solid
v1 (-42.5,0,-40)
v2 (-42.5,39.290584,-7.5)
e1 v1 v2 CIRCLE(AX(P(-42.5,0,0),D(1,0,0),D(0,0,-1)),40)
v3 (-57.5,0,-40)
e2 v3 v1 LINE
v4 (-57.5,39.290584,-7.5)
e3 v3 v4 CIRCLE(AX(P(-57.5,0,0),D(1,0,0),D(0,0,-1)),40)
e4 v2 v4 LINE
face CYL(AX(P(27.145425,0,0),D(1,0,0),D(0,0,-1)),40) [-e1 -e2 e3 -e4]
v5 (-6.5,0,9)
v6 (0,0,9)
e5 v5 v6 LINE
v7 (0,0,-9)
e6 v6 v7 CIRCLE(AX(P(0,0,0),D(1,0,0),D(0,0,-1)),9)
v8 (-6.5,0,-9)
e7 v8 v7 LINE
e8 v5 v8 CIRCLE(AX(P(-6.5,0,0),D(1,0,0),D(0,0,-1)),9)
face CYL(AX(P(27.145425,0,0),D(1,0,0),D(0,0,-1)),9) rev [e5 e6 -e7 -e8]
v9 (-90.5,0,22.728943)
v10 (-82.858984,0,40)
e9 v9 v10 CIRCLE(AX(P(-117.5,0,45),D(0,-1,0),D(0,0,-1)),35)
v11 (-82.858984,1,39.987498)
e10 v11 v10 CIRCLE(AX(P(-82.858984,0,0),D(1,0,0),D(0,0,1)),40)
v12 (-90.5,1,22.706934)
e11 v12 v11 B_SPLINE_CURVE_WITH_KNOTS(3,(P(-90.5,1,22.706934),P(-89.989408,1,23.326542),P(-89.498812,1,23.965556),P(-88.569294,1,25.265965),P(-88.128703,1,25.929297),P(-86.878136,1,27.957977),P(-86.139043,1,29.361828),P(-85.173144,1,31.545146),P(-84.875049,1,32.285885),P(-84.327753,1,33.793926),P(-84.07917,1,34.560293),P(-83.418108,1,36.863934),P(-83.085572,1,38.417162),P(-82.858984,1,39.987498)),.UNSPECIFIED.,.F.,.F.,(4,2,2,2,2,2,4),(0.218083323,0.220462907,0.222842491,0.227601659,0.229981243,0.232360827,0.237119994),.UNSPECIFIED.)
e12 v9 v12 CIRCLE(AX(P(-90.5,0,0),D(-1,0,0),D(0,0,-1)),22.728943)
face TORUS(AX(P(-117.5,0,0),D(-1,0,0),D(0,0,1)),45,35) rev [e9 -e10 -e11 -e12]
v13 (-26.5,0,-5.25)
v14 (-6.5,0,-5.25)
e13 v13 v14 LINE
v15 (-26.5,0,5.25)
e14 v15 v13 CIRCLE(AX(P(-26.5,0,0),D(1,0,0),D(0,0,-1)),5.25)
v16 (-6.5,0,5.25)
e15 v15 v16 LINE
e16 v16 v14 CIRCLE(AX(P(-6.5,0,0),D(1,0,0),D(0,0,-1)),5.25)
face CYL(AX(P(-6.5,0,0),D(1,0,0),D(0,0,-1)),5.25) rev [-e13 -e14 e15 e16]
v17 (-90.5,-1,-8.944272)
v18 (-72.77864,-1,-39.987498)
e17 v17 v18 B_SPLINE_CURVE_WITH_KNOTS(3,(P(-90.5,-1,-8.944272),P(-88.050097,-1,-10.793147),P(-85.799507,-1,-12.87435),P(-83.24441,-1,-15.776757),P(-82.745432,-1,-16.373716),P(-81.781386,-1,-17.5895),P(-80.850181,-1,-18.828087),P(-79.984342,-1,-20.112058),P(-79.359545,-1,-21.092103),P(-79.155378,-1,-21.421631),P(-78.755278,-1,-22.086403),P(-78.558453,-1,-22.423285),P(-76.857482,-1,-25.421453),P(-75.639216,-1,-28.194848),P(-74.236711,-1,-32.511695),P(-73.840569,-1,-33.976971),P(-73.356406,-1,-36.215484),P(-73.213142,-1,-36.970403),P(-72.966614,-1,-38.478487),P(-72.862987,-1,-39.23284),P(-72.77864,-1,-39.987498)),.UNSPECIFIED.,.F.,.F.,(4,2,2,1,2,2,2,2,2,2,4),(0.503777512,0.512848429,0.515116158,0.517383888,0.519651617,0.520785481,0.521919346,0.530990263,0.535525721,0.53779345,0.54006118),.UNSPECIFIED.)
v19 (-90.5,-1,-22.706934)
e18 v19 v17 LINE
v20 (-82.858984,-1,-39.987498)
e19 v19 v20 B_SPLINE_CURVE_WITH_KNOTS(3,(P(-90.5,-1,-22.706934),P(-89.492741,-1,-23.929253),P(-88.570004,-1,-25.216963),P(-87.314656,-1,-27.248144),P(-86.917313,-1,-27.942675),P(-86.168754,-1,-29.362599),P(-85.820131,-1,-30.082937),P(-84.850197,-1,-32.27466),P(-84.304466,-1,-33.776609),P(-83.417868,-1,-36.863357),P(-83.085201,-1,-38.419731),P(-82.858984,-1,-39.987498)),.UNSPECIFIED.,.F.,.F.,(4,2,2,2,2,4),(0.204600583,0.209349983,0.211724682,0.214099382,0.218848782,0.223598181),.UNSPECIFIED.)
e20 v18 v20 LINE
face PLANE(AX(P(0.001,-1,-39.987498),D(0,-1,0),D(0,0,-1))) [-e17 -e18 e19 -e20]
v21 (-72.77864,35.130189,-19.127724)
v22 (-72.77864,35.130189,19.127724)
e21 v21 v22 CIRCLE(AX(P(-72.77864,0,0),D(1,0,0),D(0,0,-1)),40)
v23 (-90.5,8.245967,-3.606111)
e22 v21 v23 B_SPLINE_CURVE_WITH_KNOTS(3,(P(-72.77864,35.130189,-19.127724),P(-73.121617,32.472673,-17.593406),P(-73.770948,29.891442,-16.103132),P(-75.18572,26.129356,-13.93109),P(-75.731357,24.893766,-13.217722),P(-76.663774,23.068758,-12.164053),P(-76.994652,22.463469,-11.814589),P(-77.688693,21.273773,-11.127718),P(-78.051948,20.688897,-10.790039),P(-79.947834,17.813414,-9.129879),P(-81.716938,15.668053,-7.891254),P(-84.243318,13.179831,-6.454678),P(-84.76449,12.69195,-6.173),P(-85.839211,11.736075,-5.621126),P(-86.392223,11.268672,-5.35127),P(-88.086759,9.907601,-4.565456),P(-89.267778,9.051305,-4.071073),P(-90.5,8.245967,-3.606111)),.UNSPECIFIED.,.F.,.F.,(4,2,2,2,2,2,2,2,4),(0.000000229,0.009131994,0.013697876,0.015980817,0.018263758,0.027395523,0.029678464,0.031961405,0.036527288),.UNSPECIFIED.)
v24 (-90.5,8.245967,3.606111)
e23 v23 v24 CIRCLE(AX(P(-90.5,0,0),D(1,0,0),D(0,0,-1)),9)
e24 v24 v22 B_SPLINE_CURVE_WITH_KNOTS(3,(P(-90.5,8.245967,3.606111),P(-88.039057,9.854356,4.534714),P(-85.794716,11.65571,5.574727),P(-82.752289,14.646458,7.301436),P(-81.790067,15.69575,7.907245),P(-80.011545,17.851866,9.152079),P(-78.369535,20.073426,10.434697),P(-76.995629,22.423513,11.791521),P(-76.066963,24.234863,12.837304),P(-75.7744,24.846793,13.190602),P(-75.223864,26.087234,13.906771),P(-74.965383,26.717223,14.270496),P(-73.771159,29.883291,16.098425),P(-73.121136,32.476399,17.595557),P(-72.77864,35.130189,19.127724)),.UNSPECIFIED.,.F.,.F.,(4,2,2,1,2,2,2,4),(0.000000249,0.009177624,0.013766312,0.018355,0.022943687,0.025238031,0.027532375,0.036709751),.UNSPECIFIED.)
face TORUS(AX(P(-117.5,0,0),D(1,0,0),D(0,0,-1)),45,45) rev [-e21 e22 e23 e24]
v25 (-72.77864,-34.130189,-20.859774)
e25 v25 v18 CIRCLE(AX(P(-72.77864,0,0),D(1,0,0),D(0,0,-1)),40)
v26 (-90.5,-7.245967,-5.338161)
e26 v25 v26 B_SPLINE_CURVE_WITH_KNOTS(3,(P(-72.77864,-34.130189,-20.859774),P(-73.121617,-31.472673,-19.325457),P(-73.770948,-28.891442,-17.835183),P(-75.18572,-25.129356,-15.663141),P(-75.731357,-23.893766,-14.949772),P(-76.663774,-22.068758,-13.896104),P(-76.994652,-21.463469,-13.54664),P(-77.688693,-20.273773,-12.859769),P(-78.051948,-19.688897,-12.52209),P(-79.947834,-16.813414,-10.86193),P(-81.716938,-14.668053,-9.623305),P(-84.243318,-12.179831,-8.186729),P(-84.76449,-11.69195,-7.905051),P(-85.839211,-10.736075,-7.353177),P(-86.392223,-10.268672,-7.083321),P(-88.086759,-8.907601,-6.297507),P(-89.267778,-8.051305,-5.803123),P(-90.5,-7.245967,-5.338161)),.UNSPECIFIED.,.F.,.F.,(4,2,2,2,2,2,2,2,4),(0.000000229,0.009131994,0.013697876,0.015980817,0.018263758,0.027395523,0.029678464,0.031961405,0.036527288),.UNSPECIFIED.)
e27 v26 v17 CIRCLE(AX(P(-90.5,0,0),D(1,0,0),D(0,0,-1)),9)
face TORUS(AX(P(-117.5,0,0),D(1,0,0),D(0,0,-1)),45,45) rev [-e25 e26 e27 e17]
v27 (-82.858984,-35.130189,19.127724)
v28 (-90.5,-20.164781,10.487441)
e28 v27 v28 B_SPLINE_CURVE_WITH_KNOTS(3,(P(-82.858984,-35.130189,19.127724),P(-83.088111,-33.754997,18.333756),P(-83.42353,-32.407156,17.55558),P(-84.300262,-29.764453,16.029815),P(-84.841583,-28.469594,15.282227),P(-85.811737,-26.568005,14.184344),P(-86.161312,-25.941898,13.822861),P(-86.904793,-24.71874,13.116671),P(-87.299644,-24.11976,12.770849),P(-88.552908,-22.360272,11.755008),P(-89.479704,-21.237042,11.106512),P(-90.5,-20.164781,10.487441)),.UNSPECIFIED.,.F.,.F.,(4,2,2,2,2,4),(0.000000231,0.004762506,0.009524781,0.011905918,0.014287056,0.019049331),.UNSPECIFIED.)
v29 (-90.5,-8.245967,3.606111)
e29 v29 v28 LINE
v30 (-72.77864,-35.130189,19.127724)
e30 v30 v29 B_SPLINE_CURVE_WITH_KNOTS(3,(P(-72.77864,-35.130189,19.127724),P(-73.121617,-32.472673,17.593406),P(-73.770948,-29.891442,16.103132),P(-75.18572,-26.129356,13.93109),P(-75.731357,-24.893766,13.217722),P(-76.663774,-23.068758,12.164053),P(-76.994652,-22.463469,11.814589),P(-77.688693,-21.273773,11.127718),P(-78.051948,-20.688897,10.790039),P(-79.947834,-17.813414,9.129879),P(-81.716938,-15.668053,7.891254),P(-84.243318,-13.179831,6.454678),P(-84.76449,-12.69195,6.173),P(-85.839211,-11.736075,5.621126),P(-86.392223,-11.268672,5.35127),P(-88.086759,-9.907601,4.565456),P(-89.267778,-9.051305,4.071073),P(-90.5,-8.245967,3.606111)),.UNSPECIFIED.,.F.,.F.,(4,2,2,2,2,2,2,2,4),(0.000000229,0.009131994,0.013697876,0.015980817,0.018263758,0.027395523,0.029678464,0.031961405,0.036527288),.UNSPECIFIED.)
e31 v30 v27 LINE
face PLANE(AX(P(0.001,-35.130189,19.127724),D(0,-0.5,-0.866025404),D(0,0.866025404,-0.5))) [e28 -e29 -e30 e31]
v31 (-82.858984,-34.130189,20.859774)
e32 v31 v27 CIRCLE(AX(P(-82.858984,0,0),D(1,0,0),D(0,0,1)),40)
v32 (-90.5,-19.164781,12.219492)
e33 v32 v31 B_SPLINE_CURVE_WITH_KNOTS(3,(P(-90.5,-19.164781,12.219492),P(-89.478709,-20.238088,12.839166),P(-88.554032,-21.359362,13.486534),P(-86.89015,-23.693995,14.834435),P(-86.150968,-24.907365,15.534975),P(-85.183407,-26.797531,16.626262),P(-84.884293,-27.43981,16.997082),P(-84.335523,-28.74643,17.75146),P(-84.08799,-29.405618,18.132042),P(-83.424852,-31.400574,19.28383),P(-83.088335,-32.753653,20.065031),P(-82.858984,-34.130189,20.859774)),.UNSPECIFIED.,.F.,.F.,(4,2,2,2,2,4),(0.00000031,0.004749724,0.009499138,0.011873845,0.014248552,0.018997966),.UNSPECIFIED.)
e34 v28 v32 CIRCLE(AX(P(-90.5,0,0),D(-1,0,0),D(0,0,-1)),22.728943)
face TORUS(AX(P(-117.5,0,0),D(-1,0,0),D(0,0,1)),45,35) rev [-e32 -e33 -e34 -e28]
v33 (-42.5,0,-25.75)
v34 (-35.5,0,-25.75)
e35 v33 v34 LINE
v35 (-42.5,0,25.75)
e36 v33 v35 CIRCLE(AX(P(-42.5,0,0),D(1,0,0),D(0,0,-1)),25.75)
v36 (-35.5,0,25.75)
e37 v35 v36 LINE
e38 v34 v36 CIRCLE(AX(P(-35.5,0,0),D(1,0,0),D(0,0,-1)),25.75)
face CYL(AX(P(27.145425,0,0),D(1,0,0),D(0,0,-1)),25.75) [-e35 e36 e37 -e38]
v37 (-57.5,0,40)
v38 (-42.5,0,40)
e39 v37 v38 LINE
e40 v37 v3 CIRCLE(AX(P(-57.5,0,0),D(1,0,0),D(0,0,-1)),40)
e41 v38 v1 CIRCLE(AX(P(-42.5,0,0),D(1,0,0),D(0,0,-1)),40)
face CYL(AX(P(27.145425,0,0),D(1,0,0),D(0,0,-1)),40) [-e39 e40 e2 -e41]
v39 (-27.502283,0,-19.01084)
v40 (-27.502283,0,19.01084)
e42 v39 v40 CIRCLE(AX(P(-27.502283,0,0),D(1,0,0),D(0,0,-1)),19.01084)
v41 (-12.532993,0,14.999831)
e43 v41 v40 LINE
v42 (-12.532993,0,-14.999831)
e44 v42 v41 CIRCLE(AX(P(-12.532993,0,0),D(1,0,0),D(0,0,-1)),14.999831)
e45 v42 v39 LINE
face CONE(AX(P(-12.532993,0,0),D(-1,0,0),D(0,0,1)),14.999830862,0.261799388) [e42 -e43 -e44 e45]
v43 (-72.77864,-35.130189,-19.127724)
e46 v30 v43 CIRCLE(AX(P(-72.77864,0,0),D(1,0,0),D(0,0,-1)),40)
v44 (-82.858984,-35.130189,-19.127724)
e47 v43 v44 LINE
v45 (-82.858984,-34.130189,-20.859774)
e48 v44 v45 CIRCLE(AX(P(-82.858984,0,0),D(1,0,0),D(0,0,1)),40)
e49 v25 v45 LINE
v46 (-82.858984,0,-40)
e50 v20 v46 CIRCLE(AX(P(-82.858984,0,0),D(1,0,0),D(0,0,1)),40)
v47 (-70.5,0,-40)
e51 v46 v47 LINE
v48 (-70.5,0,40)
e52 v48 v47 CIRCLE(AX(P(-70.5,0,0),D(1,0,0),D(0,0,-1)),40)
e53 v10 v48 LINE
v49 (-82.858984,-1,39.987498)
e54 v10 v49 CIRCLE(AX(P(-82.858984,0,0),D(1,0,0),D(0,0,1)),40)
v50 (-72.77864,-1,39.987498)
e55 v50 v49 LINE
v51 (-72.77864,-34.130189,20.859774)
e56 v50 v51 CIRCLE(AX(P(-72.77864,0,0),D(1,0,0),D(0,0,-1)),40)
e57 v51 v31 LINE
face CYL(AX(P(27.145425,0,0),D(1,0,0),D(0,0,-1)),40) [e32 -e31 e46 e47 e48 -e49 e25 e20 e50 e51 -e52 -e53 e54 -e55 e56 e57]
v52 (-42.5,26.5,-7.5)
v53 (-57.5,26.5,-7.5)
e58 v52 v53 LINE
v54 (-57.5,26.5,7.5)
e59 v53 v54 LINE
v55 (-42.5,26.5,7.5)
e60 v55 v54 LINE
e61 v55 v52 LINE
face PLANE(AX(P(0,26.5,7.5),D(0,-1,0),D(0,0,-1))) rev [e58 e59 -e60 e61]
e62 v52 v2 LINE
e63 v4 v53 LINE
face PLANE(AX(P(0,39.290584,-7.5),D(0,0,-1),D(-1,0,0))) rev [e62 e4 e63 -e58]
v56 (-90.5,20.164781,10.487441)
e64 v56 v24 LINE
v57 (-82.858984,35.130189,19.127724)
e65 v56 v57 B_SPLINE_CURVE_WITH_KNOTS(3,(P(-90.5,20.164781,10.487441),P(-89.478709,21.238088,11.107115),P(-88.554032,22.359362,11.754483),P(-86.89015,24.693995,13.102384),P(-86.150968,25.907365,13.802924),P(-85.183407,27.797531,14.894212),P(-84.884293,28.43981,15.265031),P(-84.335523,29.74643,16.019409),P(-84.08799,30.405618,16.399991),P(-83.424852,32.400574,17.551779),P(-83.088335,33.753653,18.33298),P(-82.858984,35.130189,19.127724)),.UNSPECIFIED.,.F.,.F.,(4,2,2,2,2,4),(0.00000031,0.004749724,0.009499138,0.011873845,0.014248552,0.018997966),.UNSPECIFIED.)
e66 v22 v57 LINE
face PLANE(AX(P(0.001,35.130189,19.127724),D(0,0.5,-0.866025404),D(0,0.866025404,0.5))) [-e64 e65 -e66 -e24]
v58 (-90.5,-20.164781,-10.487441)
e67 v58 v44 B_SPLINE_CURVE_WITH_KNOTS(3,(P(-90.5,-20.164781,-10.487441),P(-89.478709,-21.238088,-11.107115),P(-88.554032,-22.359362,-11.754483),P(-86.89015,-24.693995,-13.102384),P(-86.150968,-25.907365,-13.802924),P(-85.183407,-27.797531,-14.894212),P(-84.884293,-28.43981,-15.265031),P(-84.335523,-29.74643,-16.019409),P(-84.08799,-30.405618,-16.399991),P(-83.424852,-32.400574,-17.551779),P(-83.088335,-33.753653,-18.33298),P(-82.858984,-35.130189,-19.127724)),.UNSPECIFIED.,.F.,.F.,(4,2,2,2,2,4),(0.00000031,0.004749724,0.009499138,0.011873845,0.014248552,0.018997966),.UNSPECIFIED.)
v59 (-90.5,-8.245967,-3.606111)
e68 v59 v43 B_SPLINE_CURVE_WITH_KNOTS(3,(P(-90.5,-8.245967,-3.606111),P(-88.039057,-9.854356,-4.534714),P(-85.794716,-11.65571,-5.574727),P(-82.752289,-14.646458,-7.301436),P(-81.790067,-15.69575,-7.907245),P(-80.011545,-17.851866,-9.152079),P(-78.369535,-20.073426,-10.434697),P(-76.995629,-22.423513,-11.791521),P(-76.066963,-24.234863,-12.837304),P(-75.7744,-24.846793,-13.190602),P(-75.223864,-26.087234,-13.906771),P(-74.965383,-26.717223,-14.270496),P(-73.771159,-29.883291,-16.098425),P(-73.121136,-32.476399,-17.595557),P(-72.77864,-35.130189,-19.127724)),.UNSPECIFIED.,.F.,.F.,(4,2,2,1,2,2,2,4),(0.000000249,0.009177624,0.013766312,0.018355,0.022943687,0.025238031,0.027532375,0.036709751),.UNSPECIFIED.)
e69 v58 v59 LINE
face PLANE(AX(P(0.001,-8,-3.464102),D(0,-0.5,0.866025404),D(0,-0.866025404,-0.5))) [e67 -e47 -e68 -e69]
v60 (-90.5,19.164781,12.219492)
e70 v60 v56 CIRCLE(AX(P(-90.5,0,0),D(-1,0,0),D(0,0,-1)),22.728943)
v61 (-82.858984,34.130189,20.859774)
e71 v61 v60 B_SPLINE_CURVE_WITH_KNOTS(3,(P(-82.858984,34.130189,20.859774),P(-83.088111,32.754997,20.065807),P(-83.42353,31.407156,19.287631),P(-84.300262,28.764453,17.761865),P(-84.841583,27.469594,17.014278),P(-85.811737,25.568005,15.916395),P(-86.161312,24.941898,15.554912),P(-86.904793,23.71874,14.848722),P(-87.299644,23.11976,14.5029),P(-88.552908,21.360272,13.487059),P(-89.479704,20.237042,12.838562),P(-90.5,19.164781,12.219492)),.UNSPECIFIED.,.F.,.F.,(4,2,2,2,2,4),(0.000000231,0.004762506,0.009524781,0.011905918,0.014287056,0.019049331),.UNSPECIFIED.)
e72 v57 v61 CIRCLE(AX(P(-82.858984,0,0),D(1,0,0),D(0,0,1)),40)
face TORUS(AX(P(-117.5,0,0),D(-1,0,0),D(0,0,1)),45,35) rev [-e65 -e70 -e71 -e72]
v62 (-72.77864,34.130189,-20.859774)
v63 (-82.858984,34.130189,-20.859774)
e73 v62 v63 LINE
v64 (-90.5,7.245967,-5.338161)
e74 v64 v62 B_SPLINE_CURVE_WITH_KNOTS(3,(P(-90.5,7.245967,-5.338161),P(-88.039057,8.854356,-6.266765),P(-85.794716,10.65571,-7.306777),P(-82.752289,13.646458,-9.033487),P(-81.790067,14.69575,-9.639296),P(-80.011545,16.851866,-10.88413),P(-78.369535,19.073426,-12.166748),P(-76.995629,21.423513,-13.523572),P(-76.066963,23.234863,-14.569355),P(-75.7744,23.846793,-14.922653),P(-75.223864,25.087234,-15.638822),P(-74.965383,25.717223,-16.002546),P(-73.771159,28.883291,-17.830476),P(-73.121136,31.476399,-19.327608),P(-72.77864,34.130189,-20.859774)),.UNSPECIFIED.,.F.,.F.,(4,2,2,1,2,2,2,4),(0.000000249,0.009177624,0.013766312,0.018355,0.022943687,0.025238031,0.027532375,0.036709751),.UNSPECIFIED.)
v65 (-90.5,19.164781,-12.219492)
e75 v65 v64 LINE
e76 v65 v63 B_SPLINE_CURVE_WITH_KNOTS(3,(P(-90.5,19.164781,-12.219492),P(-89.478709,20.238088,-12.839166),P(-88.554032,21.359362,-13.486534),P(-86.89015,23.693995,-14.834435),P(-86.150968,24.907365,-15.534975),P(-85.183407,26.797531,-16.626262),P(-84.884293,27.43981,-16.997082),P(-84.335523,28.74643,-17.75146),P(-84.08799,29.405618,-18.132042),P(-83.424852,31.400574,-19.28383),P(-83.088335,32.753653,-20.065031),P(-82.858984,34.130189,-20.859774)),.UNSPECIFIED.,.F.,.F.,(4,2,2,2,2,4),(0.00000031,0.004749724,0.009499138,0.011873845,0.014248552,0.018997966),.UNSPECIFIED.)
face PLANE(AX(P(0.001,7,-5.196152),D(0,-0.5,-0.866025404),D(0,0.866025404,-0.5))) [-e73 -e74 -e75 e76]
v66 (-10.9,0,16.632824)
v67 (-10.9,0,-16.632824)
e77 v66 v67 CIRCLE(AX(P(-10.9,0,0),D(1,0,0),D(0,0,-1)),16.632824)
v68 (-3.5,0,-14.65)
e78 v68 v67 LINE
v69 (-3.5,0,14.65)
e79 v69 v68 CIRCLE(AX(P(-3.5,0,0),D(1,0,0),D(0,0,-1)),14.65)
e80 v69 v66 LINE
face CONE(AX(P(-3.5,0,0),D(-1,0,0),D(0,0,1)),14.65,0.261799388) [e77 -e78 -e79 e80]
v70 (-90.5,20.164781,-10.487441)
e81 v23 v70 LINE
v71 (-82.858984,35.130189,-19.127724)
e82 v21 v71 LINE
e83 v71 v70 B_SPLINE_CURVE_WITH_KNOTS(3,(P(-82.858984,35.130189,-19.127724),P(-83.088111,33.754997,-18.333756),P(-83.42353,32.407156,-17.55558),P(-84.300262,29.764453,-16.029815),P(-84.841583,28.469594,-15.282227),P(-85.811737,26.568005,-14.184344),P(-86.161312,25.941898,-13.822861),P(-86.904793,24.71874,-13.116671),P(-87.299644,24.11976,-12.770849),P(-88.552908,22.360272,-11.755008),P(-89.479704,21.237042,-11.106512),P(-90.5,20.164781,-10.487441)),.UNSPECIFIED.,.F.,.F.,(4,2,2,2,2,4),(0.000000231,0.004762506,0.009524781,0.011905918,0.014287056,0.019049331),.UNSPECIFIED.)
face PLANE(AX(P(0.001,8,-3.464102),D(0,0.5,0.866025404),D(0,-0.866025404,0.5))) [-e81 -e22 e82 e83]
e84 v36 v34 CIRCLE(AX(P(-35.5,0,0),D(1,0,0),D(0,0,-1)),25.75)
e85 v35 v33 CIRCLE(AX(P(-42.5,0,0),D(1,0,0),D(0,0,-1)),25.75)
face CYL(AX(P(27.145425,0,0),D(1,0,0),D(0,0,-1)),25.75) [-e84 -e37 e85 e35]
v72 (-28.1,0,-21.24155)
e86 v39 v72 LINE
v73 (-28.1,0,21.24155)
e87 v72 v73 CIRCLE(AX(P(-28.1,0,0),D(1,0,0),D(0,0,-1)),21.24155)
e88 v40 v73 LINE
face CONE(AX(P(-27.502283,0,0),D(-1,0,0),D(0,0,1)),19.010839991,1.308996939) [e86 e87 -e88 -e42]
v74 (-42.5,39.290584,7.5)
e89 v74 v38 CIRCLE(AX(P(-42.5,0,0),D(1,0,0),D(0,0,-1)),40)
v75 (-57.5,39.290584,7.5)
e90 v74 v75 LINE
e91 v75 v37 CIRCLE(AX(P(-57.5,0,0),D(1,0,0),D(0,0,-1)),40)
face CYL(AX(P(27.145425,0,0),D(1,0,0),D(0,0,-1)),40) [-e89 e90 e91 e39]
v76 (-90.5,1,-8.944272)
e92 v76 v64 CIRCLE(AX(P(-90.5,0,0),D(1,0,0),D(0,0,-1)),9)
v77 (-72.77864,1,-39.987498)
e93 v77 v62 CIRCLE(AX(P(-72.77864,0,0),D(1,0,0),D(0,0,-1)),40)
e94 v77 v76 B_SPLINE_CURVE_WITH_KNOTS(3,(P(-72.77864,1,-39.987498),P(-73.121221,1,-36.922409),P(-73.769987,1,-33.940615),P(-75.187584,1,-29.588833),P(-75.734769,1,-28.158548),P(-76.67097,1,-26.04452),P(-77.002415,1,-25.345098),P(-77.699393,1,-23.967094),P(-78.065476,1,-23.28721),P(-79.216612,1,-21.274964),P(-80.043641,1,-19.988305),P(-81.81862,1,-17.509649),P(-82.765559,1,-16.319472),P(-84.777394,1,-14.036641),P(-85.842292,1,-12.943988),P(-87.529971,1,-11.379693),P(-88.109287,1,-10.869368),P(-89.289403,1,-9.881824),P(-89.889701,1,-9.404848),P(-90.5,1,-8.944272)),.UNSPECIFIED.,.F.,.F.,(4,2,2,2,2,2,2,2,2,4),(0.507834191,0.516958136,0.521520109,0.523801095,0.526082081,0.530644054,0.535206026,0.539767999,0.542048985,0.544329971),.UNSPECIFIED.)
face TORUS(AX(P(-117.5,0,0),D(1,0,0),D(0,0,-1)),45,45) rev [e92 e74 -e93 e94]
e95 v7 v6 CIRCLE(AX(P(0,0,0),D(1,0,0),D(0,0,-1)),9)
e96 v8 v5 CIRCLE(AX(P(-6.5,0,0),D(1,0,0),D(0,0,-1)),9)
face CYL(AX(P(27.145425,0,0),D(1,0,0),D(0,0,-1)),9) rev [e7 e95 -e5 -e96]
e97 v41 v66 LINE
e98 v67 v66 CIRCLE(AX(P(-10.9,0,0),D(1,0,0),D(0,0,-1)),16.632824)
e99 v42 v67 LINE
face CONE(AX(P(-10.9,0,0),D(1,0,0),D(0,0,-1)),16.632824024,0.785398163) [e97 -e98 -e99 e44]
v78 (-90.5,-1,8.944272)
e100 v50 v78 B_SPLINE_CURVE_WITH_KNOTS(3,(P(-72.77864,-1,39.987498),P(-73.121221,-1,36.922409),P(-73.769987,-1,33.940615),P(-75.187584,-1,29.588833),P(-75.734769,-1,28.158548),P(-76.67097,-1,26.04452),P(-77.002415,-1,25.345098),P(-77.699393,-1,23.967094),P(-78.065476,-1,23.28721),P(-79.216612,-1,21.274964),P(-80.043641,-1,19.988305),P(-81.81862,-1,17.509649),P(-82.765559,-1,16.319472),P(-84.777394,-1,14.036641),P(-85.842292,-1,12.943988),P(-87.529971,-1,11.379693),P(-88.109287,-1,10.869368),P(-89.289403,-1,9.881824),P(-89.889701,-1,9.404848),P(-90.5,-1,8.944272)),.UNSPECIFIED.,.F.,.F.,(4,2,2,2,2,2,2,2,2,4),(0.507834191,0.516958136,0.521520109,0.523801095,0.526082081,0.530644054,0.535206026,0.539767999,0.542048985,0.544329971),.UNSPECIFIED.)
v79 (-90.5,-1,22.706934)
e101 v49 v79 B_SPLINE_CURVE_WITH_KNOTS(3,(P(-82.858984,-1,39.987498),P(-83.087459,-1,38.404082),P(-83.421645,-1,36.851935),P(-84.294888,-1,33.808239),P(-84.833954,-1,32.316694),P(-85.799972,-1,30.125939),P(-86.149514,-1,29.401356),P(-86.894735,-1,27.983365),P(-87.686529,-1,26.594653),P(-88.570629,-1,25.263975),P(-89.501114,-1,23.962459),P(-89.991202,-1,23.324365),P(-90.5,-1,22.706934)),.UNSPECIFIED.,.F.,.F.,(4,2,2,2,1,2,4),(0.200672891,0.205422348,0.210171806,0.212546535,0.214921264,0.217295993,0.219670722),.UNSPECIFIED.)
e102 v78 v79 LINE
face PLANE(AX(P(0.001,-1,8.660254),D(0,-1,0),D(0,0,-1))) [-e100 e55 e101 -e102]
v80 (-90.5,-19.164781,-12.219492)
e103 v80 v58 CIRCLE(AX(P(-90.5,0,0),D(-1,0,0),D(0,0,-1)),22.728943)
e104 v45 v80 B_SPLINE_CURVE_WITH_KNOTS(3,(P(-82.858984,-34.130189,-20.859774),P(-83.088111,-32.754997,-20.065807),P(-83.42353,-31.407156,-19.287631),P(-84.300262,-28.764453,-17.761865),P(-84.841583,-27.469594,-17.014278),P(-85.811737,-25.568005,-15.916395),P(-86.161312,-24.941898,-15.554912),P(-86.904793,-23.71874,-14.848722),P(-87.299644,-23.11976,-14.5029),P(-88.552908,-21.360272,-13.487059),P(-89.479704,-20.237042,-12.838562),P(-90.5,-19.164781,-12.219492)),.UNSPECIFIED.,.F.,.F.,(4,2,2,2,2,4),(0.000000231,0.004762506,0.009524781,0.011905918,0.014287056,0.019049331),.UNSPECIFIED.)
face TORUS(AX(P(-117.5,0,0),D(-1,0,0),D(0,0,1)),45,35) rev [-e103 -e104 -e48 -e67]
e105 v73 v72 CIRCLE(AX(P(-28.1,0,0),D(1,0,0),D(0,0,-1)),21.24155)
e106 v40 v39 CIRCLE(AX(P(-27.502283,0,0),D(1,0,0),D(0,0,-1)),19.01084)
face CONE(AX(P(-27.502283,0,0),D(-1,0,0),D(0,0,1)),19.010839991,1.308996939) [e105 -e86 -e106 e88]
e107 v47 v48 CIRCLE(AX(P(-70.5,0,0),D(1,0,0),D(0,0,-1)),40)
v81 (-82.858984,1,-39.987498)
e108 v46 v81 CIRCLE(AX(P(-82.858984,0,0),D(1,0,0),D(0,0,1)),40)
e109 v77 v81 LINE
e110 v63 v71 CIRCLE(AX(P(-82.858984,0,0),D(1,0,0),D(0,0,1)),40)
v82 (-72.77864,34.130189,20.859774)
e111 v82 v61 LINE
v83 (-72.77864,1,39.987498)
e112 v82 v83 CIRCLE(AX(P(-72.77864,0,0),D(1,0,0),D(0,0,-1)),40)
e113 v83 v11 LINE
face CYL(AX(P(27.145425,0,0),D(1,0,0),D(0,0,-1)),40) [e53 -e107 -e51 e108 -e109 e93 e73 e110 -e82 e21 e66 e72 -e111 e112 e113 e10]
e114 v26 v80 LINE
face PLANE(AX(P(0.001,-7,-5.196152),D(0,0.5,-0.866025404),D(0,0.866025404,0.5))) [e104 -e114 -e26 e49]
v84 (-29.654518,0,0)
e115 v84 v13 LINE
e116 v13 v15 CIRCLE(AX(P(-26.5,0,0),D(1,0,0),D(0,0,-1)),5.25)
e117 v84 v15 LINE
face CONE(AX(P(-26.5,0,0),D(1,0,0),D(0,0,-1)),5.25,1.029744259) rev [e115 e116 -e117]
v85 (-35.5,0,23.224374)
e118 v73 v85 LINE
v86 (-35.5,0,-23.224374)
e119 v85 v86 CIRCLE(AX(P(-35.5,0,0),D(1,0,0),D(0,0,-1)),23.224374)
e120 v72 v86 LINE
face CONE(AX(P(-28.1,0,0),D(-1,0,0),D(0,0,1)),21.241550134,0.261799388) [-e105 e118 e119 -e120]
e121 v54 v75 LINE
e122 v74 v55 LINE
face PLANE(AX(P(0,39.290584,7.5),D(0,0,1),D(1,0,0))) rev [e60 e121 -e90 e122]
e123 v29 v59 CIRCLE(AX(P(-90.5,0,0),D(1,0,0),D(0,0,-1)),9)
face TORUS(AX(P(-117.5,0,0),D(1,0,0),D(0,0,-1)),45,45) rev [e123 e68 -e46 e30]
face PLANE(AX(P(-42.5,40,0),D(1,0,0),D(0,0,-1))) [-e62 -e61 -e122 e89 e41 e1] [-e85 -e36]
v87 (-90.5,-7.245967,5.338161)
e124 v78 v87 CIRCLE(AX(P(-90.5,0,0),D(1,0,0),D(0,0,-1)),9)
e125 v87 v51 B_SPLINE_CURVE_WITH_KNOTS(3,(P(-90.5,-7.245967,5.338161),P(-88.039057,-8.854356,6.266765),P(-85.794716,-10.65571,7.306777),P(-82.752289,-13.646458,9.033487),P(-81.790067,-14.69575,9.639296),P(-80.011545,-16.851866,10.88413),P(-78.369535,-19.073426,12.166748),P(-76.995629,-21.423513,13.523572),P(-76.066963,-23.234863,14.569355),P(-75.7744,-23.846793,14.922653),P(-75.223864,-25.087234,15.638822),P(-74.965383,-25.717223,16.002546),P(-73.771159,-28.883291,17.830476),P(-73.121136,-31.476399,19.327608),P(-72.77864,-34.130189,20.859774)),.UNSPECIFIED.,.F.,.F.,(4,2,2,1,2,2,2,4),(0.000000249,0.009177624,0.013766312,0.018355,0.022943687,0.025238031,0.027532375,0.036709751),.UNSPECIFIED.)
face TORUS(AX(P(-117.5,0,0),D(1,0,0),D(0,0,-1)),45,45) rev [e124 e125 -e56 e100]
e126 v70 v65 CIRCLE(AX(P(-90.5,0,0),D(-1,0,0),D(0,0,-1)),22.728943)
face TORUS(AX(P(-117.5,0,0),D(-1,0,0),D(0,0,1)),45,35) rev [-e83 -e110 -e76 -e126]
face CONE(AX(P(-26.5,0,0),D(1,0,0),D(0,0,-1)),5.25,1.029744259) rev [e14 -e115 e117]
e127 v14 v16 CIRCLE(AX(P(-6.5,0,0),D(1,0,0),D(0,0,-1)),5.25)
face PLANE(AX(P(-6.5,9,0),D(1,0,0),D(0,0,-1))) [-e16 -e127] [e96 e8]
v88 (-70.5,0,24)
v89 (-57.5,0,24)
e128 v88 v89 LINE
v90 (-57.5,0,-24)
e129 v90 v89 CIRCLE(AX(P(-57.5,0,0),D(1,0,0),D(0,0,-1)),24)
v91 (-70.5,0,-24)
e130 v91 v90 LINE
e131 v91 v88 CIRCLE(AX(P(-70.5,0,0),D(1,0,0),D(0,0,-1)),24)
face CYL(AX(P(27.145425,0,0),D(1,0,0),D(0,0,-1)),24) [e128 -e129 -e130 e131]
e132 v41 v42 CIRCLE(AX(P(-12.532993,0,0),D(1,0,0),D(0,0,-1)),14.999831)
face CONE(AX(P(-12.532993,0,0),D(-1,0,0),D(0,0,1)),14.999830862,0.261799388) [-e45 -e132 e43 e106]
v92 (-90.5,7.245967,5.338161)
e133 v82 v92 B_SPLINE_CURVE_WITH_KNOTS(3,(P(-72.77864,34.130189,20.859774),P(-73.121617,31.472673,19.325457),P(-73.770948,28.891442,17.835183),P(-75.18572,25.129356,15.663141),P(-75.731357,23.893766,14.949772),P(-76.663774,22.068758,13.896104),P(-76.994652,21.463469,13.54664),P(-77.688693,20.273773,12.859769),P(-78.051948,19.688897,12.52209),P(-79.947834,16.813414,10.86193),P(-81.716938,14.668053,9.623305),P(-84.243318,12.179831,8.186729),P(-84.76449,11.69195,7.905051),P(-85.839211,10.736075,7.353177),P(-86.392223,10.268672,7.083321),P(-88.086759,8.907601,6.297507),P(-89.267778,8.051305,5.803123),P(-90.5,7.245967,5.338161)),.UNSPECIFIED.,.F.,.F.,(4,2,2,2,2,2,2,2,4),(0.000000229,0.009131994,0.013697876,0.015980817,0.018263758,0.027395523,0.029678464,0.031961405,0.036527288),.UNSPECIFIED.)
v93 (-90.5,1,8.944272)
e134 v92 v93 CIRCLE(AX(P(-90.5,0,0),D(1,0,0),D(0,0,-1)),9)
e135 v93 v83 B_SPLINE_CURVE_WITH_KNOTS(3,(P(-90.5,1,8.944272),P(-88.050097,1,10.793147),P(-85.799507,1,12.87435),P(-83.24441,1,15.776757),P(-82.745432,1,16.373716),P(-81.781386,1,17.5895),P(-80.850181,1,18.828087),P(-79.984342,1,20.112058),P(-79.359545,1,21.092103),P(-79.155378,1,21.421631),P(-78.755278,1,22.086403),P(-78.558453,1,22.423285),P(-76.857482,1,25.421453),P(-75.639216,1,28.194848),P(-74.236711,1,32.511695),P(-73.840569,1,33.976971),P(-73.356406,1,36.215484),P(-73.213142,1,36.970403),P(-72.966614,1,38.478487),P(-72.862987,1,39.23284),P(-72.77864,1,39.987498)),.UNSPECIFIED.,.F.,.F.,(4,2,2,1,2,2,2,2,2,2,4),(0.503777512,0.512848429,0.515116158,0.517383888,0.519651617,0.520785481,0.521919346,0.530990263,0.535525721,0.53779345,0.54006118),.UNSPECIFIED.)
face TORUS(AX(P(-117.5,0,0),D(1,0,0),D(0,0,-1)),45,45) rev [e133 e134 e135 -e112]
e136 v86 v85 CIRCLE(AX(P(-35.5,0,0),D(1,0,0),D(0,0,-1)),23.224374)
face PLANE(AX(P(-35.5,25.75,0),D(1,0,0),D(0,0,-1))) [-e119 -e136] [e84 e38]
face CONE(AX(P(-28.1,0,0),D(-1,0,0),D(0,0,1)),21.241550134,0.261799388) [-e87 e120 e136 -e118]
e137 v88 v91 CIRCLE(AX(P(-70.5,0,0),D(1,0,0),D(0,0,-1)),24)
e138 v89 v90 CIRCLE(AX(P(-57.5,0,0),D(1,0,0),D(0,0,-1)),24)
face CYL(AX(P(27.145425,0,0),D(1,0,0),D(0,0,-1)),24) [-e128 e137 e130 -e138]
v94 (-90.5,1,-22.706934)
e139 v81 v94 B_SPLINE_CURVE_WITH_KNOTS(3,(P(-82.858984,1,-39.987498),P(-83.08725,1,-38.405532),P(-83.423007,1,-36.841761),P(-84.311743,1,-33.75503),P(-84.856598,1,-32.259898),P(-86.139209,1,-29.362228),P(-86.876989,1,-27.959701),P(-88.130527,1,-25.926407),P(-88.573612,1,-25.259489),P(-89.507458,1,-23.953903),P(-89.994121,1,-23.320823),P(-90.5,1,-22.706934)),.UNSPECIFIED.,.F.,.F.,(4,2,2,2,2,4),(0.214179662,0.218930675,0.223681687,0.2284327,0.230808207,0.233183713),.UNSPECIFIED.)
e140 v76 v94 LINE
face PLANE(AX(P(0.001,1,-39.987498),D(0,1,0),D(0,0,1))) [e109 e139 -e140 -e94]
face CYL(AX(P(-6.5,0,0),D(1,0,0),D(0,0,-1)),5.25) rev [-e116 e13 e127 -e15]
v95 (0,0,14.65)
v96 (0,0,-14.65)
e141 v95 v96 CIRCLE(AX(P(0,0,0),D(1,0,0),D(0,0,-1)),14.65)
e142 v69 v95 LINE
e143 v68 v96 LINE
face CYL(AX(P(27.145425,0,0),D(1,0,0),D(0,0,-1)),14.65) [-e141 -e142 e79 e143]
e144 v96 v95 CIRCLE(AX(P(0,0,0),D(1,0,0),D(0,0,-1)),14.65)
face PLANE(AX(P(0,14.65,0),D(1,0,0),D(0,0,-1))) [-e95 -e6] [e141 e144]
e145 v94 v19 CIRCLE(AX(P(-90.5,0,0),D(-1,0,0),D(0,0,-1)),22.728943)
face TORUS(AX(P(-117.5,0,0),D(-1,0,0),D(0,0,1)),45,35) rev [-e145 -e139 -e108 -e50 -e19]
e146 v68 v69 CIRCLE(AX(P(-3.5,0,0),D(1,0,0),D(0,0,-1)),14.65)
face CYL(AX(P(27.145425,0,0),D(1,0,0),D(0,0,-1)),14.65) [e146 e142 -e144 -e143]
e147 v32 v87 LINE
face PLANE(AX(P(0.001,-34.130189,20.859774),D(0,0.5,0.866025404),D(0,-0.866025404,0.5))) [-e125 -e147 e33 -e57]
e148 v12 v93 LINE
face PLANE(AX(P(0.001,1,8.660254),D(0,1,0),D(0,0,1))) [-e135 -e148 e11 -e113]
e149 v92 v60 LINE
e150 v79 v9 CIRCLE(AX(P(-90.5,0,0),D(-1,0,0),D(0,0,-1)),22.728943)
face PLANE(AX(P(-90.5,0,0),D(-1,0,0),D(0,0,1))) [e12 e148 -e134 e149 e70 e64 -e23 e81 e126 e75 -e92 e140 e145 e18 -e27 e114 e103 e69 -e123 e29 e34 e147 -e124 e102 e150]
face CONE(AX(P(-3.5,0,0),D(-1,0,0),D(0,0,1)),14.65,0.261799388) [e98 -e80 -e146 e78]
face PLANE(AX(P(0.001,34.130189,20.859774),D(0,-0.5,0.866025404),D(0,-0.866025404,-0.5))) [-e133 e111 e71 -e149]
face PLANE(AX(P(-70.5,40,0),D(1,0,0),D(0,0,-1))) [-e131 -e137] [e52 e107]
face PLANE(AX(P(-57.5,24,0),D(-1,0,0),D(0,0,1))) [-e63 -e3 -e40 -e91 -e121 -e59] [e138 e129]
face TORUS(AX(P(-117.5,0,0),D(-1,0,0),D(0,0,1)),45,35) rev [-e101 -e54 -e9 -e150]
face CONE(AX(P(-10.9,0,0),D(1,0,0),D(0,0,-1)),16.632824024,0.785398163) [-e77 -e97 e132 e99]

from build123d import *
from build123d.topology import SkipClean

# Parameters (mm, degrees)
M12X1_5_TAPPED_HOLE1_D     = 10.5
M12X1_5_TAPPED_HOLE1_DEPTH = 20
M12X1_5_TAPPED_HOLE1_TIP   = 3.15451825
CUT_EXTRUDE1_DEPTH         = 81.661329124
BOSS_EXTRUDE1_REACH        = 108.725
SKETCH6_R                  = 35


with BuildPart() as part:
    # Sketch1 → Revolve1 (revolve)
    with BuildSketch(Plane.XY, mode=Mode.PRIVATE) as revolve1_sk:
        with BuildLine():
            Line((-6.5, 0), (-90.5, 0))
            Line((-90.5, 0), (-90.5, 9))
            ThreePointArc((-90.5, 9), (-78.432899341, 22.667027827), (-72.77864045, 40))
            Line((-72.77864045, 40), (-70.5, 40))
            Line((-70.5, 40), (-70.5, 24))
            Line((-70.5, 24), (-57.5, 24))
            Line((-57.5, 24), (-57.5, 40))
            Line((-57.5, 40), (-42.5, 40))
            Line((-42.5, 40), (-42.5, 25.75))
            Line((-42.5, 25.75), (-35.5, 25.75))
            Line((-35.5, 25.75), (-35.5, 23.224374158))
            Line((-35.5, 23.224374158), (-28.1, 21.241550134))
            Line((-28.1, 21.241550134), (-27.502283019, 19.010839991))
            Line((-27.502283019, 19.010839991), (-12.532993162, 14.999830862))
            Line((-12.532993162, 14.999830862), (-10.9, 16.632824024))
            Line((-10.9, 16.632824024), (-3.5, 14.65))
            Line((-3.5, 14.65), (0, 14.65))
            Line((0, 14.65), (0, 9))
            Line((0, 9), (-6.5, 9))
            Line((-6.5, 9), (-6.5, 0))
        make_face()
    revolve(revolve1_sk.sketch.rotate(Axis((27.145425235, 0, 0), (-1, 0, 0)), 90), axis=Axis((27.145425235, 0, 0), (-1, 0, 0)))

    # M12x1.5 Tapped Hole1
    with Locations(Plane(origin=(-6.5, 0, 0), x_dir=(0, 0, -1), z_dir=(1, 0, 0))):
        with Locations((0, 0)):
            Hole(M12X1_5_TAPPED_HOLE1_D / 2, depth=M12X1_5_TAPPED_HOLE1_DEPTH)
            with Locations((0, 0, -(M12X1_5_TAPPED_HOLE1_DEPTH + M12X1_5_TAPPED_HOLE1_TIP / 2))):  # 118° drill point
                Cone(0, M12X1_5_TAPPED_HOLE1_D / 2, M12X1_5_TAPPED_HOLE1_TIP, mode=Mode.SUBTRACT)

    # Sketch4 → Cut-Extrude1 (cut, through all)
    with BuildSketch(Plane.ZY.offset(57.5)):
        with BuildLine():
            Line((-7.5, 39.290584114), (-7.5, 26.5))
            Line((-7.5, 26.5), (7.5, 26.5))
            Line((7.5, 26.5), (7.5, 39.290584114))
            ThreePointArc((7.5, 39.290584114), (0, 40), (-7.5, 39.290584114))
        make_face()
    extrude(amount=-CUT_EXTRUDE1_DEPTH, mode=Mode.SUBTRACT)

    # Sketch5 → Boss-Extrude1 (add, up to next)
    with BuildSketch(Plane.ZY.offset(90.5), mode=Mode.PRIVATE) as boss_extrude1_sk1:
        with BuildLine():
            ThreePointArc((20.859774427, 34.130189142), (20, 34.641016151), (19.127723619, 35.130189142))
            Line((19.127723619, 35.130189142), (3.606110551, 8.245966692))
            ThreePointArc((3.606110551, 8.245966692), (4.5, 7.794228634), (5.338161359, 7.245966692))
            Line((5.338161359, 7.245966692), (20.859774427, 34.130189142))
        make_face()
    boss_extrude1_tool1 = extrude(boss_extrude1_sk1.sketch, amount=-BOSS_EXTRUDE1_REACH, mode=Mode.PRIVATE) - part.part
    # Sketch5 → Boss-Extrude1 (add, up to next)
    with BuildSketch(Plane.ZY.offset(90.5), mode=Mode.PRIVATE) as boss_extrude1_sk2:
        with BuildLine():
            ThreePointArc((-5.338161359, 7.245966692), (-4.5, 7.794228634), (-3.606110551, 8.245966692))
            Line((-3.606110551, 8.245966692), (-19.127723619, 35.130189142))
            ThreePointArc((-19.127723619, 35.130189142), (-20, 34.641016151), (-20.859774427, 34.130189142))
            Line((-20.859774427, 34.130189142), (-5.338161359, 7.245966692))
        make_face()
    boss_extrude1_tool2 = extrude(boss_extrude1_sk2.sketch, amount=-BOSS_EXTRUDE1_REACH, mode=Mode.PRIVATE) - part.part
    # Sketch5 → Boss-Extrude1 (add, up to next)
    with BuildSketch(Plane.ZY.offset(90.5), mode=Mode.PRIVATE) as boss_extrude1_sk3:
        with BuildLine():
            Line((39.987498046, 1), (8.94427191, 1))
            ThreePointArc((8.94427191, 1), (9, 0), (8.94427191, -1))
            Line((8.94427191, -1), (39.987498046, -1))
            ThreePointArc((39.987498046, -1), (40, 0), (39.987498046, 1))
        make_face()
    boss_extrude1_tool3 = extrude(boss_extrude1_sk3.sketch, amount=-BOSS_EXTRUDE1_REACH, mode=Mode.PRIVATE) - part.part
    # Sketch5 → Boss-Extrude1 (add, up to next)
    with BuildSketch(Plane.ZY.offset(90.5), mode=Mode.PRIVATE) as boss_extrude1_sk4:
        with BuildLine():
            ThreePointArc((-8.94427191, -1), (-9, 0), (-8.94427191, 1))
            Line((-8.94427191, 1), (-39.987498046, 1))
            ThreePointArc((-39.987498046, 1), (-40, 0), (-39.987498046, -1))
            Line((-39.987498046, -1), (-8.94427191, -1))
        make_face()
    boss_extrude1_tool4 = extrude(boss_extrude1_sk4.sketch, amount=-BOSS_EXTRUDE1_REACH, mode=Mode.PRIVATE) - part.part
    # Sketch5 → Boss-Extrude1 (add, up to next)
    with BuildSketch(Plane.ZY.offset(90.5), mode=Mode.PRIVATE) as boss_extrude1_sk5:
        with BuildLine():
            Line((20.859774427, -34.130189142), (5.338161359, -7.245966692))
            ThreePointArc((5.338161359, -7.245966692), (4.5, -7.794228634), (3.606110551, -8.245966692))
            Line((3.606110551, -8.245966692), (19.127723619, -35.130189142))
            ThreePointArc((19.127723619, -35.130189142), (20, -34.641016151), (20.859774427, -34.130189142))
        make_face()
    boss_extrude1_tool5 = extrude(boss_extrude1_sk5.sketch, amount=-BOSS_EXTRUDE1_REACH, mode=Mode.PRIVATE) - part.part
    # Sketch5 → Boss-Extrude1 (add, up to next)
    with BuildSketch(Plane.ZY.offset(90.5), mode=Mode.PRIVATE) as boss_extrude1_sk6:
        with BuildLine():
            ThreePointArc((-3.606110551, -8.245966692), (-4.5, -7.794228634), (-5.338161359, -7.245966692))
            Line((-5.338161359, -7.245966692), (-20.859774427, -34.130189142))
            ThreePointArc((-20.859774427, -34.130189142), (-20, -34.641016151), (-19.127723619, -35.130189142))
            Line((-19.127723619, -35.130189142), (-3.606110551, -8.245966692))
        make_face()
    boss_extrude1_tool6 = extrude(boss_extrude1_sk6.sketch, amount=-BOSS_EXTRUDE1_REACH, mode=Mode.PRIVATE) - part.part
    add(boss_extrude1_tool1.solids().sort_by_distance((-90.5, 21.207781, 12.244318))[0])
    add(boss_extrude1_tool2.solids().sort_by_distance((-90.5, 21.207781, -12.244318))[0])
    add(boss_extrude1_tool3.solids().sort_by_distance((-90.5, 0, 24.488636))[0])
    add(boss_extrude1_tool4.solids().sort_by_distance((-90.5, 0, -24.488636))[0])
    add(boss_extrude1_tool5.solids().sort_by_distance((-90.5, -21.207781, 12.244318))[0])
    add(boss_extrude1_tool6.solids().sort_by_distance((-90.5, -21.207781, -12.244318))[0])

    # Sketch6 → Cut-Revolve1 (revolve, cut)
    with SkipClean():  # the faces are left unmerged after this step: merging them gives an invalid solid
        with BuildSketch(Plane.XY, mode=Mode.PRIVATE) as cut_revolve1_sk:
            with Locations((-117.5, 45)):
                Circle(SKETCH6_R)
        revolve(cut_revolve1_sk.sketch.rotate(Axis((-117.5, 0, 0), (1, 0, 0)), 270), axis=Axis((-117.5, 0, 0), (1, 0, 0)), mode=Mode.SUBTRACT)


solid = part.part
